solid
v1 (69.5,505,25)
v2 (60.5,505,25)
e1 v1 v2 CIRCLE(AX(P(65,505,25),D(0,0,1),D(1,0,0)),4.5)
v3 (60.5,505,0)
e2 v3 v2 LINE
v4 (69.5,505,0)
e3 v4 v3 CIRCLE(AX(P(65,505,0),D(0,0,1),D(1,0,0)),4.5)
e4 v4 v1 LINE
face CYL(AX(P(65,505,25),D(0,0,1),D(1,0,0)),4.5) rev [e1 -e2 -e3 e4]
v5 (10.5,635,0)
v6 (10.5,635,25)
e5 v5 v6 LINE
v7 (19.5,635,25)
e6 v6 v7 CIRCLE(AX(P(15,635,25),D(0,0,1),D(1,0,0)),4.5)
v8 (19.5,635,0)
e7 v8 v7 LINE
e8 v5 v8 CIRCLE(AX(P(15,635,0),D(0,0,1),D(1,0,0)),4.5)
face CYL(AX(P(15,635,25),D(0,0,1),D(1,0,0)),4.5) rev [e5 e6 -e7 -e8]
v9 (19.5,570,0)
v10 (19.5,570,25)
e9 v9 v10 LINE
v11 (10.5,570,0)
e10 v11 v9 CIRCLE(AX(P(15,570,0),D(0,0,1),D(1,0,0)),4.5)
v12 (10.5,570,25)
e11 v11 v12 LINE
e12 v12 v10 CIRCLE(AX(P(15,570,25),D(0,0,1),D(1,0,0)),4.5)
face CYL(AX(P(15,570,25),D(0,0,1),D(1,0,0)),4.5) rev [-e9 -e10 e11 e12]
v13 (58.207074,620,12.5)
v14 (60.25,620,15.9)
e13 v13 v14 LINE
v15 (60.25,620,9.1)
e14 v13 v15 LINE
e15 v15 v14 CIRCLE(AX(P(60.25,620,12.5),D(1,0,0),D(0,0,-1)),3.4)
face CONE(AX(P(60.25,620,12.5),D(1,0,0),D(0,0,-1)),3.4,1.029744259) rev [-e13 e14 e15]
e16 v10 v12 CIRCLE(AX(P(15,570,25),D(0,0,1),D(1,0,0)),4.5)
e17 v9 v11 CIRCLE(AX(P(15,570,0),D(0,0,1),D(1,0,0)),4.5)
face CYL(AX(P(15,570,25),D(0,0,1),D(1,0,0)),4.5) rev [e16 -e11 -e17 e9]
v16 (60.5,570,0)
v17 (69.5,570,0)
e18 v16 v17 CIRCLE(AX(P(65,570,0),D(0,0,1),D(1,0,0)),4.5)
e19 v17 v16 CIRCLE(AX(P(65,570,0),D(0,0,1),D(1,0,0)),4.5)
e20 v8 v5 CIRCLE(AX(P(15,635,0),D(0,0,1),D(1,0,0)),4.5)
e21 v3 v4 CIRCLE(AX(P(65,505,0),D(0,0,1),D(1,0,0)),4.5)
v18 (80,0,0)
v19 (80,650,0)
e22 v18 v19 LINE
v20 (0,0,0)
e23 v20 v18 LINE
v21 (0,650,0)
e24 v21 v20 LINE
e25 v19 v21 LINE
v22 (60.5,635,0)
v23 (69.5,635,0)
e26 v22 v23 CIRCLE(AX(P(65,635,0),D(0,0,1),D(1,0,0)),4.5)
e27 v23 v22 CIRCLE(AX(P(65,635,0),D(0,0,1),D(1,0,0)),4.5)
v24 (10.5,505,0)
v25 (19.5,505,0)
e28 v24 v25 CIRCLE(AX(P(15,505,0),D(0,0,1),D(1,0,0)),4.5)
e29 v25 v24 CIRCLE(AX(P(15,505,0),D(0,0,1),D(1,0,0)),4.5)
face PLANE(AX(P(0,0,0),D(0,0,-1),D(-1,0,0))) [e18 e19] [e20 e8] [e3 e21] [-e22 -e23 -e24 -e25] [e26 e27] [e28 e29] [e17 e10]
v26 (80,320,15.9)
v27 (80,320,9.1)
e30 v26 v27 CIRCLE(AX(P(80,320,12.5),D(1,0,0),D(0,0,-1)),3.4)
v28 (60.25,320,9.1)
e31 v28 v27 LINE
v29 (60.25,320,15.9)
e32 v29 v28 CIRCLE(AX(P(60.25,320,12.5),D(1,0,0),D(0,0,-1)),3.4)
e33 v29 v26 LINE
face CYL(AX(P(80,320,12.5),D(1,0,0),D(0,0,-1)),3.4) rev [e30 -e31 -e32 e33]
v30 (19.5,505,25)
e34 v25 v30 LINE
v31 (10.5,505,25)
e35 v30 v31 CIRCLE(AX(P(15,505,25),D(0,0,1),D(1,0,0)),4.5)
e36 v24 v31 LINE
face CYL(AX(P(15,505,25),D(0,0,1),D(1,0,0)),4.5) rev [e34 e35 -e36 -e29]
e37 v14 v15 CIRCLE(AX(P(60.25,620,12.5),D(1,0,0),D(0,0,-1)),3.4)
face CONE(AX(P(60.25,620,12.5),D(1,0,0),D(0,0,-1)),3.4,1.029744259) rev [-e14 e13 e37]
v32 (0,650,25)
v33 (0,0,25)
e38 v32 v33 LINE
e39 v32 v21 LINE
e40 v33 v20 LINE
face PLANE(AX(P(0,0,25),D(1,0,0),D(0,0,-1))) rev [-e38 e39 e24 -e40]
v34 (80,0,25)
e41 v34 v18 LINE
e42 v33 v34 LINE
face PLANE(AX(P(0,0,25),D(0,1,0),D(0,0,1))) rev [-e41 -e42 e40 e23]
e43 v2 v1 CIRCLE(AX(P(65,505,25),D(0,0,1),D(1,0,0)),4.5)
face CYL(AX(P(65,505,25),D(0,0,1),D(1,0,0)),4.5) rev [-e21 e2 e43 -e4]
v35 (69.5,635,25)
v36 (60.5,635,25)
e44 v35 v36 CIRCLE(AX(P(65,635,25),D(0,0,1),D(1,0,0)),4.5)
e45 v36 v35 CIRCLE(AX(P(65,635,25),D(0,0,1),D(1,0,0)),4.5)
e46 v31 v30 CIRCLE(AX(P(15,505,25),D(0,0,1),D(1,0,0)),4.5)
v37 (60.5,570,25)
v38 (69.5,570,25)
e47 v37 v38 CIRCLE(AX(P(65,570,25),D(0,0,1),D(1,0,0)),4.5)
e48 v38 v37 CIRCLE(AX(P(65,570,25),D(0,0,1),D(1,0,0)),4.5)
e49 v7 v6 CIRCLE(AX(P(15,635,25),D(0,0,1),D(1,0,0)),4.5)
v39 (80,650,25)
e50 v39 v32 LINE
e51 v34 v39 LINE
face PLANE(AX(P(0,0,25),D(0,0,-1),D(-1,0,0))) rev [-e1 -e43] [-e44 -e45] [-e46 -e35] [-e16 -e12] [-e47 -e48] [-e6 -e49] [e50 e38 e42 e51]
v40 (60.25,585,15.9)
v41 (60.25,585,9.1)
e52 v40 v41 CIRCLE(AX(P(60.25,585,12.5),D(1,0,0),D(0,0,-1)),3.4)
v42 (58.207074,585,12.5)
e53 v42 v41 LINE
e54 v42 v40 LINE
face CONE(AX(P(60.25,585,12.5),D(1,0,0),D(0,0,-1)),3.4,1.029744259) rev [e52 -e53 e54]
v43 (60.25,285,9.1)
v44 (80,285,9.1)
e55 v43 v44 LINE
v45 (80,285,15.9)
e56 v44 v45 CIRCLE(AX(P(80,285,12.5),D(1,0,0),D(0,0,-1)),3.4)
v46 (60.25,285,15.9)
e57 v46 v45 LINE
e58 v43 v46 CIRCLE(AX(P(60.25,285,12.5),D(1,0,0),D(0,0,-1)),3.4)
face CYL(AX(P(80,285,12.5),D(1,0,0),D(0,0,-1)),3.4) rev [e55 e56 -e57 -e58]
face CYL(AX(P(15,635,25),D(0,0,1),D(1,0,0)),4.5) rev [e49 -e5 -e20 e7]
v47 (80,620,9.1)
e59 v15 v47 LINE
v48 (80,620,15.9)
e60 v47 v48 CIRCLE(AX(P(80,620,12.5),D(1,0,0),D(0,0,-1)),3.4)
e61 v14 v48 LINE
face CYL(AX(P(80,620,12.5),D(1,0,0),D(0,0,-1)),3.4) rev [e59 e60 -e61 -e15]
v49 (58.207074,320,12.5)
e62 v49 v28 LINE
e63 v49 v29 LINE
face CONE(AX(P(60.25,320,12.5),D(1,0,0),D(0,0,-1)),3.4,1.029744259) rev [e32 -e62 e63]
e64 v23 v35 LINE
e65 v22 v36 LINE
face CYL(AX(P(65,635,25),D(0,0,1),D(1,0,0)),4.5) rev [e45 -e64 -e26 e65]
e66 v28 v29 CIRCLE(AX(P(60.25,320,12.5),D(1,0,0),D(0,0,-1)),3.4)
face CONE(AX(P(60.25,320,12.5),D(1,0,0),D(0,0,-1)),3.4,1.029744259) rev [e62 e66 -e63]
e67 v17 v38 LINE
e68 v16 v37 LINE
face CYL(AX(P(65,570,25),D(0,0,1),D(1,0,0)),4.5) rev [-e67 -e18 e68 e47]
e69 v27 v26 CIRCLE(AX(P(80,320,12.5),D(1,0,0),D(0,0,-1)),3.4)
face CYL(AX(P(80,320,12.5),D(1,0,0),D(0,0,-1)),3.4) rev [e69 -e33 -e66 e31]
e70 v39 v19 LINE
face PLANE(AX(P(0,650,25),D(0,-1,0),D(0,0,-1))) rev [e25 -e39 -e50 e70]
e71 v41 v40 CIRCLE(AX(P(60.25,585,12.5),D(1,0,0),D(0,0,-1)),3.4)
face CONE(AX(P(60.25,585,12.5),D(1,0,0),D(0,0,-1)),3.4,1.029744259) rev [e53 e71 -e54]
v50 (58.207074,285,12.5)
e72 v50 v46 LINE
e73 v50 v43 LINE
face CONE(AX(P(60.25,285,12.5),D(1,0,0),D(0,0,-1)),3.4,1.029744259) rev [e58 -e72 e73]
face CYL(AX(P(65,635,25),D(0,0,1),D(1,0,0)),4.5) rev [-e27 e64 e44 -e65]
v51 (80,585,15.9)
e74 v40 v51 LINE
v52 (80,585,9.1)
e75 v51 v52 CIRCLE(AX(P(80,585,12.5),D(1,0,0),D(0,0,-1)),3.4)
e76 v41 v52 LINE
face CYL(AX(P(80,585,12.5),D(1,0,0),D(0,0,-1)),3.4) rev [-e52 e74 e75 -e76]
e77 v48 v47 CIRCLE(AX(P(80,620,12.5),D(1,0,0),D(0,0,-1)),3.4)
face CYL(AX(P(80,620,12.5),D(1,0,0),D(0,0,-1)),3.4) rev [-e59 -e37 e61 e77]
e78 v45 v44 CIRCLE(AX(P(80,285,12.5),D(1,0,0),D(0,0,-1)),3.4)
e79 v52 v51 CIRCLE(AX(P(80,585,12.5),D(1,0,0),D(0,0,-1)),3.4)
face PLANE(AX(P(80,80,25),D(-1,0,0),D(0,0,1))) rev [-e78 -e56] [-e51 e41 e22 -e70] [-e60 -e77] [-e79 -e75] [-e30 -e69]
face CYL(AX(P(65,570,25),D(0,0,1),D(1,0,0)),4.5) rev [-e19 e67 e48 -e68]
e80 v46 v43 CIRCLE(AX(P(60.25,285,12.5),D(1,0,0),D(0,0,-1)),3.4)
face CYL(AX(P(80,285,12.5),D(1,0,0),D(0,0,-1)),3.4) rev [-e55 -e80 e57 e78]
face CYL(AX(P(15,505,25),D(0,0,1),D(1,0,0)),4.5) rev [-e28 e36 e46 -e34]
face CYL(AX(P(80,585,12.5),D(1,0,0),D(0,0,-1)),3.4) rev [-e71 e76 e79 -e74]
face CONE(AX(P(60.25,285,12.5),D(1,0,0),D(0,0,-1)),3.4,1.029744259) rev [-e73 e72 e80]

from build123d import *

# Parameters (mm, degrees)
BOSS_EXTRUDE1_DEPTH        = 25
F_9_0_9_DIAMETER_HOLE1_D   = 9
M8_TAPPED_HOLE1_AT_2_COUNT = 2
M8_TAPPED_HOLE1_AT_2_PITCH = 35
LPATTERN1_COUNT            = 2
LPATTERN1_PITCH            = 300


with BuildPart() as part:
    # Sketch1 → Boss-Extrude1 (new body)
    with BuildSketch(Plane.XY):
        Polygon((80, 0), (80, 80), (80, 650), (0, 650), (0, 0), align=None)
    extrude(amount=BOSS_EXTRUDE1_DEPTH)

    # Ø9.0 (9) Diameter Hole1 (through all)
    with Locations(Plane(origin=(15, 635, 25), x_dir=(1, 0, 0), z_dir=(0, 0, 1))):
        with Locations((0, 0), (50, 0), (0, -130), (50, -130), (0, -65), (50, -65)):
            Hole(F_9_0_9_DIAMETER_HOLE1_D / 2)

    # Sketch4 → M8 Tapped Hole1 (revolve, cut)
    with BuildSketch(Plane(origin=(80, 620, 12.5), x_dir=(0, 0, -1), z_dir=(0, 1, 0))):
        Polygon((0, 0), (0, 21.792926105), (3.4, 19.75), (3.4, 0), align=None)
    m8_tapped_hole1 = revolve(axis=Axis((86.35, 620, 12.5), (-1, 0, 0)), mode=Mode.SUBTRACT)

    # M8 Tapped Hole1 at 2: M8 Tapped Hole1 ×2
    with Locations(*[(0, -i * M8_TAPPED_HOLE1_AT_2_PITCH, 0) for i in range(1, M8_TAPPED_HOLE1_AT_2_COUNT)]):
        add(m8_tapped_hole1, mode=Mode.SUBTRACT)

    # LPattern1: M8 Tapped Hole1 ×2
    with Locations(*[(0, -i * LPATTERN1_PITCH, 0) for i in range(1, LPATTERN1_COUNT)]):
        add(m8_tapped_hole1, mode=Mode.SUBTRACT)

    # LPattern1 copy 1 sketch → LPattern1 copy 1 (revolve, cut)
    with BuildSketch(Plane(origin=(80, 285, 12.5), x_dir=(0, 0, -1), z_dir=(0, 1, 0))):
        Polygon((0, 0), (0, 21.792926105), (3.4, 19.75), (3.4, 0), align=None)
    revolve(axis=Axis((86.35, 285, 12.5), (-1, 0, 0)), mode=Mode.SUBTRACT)


solid = part.part
